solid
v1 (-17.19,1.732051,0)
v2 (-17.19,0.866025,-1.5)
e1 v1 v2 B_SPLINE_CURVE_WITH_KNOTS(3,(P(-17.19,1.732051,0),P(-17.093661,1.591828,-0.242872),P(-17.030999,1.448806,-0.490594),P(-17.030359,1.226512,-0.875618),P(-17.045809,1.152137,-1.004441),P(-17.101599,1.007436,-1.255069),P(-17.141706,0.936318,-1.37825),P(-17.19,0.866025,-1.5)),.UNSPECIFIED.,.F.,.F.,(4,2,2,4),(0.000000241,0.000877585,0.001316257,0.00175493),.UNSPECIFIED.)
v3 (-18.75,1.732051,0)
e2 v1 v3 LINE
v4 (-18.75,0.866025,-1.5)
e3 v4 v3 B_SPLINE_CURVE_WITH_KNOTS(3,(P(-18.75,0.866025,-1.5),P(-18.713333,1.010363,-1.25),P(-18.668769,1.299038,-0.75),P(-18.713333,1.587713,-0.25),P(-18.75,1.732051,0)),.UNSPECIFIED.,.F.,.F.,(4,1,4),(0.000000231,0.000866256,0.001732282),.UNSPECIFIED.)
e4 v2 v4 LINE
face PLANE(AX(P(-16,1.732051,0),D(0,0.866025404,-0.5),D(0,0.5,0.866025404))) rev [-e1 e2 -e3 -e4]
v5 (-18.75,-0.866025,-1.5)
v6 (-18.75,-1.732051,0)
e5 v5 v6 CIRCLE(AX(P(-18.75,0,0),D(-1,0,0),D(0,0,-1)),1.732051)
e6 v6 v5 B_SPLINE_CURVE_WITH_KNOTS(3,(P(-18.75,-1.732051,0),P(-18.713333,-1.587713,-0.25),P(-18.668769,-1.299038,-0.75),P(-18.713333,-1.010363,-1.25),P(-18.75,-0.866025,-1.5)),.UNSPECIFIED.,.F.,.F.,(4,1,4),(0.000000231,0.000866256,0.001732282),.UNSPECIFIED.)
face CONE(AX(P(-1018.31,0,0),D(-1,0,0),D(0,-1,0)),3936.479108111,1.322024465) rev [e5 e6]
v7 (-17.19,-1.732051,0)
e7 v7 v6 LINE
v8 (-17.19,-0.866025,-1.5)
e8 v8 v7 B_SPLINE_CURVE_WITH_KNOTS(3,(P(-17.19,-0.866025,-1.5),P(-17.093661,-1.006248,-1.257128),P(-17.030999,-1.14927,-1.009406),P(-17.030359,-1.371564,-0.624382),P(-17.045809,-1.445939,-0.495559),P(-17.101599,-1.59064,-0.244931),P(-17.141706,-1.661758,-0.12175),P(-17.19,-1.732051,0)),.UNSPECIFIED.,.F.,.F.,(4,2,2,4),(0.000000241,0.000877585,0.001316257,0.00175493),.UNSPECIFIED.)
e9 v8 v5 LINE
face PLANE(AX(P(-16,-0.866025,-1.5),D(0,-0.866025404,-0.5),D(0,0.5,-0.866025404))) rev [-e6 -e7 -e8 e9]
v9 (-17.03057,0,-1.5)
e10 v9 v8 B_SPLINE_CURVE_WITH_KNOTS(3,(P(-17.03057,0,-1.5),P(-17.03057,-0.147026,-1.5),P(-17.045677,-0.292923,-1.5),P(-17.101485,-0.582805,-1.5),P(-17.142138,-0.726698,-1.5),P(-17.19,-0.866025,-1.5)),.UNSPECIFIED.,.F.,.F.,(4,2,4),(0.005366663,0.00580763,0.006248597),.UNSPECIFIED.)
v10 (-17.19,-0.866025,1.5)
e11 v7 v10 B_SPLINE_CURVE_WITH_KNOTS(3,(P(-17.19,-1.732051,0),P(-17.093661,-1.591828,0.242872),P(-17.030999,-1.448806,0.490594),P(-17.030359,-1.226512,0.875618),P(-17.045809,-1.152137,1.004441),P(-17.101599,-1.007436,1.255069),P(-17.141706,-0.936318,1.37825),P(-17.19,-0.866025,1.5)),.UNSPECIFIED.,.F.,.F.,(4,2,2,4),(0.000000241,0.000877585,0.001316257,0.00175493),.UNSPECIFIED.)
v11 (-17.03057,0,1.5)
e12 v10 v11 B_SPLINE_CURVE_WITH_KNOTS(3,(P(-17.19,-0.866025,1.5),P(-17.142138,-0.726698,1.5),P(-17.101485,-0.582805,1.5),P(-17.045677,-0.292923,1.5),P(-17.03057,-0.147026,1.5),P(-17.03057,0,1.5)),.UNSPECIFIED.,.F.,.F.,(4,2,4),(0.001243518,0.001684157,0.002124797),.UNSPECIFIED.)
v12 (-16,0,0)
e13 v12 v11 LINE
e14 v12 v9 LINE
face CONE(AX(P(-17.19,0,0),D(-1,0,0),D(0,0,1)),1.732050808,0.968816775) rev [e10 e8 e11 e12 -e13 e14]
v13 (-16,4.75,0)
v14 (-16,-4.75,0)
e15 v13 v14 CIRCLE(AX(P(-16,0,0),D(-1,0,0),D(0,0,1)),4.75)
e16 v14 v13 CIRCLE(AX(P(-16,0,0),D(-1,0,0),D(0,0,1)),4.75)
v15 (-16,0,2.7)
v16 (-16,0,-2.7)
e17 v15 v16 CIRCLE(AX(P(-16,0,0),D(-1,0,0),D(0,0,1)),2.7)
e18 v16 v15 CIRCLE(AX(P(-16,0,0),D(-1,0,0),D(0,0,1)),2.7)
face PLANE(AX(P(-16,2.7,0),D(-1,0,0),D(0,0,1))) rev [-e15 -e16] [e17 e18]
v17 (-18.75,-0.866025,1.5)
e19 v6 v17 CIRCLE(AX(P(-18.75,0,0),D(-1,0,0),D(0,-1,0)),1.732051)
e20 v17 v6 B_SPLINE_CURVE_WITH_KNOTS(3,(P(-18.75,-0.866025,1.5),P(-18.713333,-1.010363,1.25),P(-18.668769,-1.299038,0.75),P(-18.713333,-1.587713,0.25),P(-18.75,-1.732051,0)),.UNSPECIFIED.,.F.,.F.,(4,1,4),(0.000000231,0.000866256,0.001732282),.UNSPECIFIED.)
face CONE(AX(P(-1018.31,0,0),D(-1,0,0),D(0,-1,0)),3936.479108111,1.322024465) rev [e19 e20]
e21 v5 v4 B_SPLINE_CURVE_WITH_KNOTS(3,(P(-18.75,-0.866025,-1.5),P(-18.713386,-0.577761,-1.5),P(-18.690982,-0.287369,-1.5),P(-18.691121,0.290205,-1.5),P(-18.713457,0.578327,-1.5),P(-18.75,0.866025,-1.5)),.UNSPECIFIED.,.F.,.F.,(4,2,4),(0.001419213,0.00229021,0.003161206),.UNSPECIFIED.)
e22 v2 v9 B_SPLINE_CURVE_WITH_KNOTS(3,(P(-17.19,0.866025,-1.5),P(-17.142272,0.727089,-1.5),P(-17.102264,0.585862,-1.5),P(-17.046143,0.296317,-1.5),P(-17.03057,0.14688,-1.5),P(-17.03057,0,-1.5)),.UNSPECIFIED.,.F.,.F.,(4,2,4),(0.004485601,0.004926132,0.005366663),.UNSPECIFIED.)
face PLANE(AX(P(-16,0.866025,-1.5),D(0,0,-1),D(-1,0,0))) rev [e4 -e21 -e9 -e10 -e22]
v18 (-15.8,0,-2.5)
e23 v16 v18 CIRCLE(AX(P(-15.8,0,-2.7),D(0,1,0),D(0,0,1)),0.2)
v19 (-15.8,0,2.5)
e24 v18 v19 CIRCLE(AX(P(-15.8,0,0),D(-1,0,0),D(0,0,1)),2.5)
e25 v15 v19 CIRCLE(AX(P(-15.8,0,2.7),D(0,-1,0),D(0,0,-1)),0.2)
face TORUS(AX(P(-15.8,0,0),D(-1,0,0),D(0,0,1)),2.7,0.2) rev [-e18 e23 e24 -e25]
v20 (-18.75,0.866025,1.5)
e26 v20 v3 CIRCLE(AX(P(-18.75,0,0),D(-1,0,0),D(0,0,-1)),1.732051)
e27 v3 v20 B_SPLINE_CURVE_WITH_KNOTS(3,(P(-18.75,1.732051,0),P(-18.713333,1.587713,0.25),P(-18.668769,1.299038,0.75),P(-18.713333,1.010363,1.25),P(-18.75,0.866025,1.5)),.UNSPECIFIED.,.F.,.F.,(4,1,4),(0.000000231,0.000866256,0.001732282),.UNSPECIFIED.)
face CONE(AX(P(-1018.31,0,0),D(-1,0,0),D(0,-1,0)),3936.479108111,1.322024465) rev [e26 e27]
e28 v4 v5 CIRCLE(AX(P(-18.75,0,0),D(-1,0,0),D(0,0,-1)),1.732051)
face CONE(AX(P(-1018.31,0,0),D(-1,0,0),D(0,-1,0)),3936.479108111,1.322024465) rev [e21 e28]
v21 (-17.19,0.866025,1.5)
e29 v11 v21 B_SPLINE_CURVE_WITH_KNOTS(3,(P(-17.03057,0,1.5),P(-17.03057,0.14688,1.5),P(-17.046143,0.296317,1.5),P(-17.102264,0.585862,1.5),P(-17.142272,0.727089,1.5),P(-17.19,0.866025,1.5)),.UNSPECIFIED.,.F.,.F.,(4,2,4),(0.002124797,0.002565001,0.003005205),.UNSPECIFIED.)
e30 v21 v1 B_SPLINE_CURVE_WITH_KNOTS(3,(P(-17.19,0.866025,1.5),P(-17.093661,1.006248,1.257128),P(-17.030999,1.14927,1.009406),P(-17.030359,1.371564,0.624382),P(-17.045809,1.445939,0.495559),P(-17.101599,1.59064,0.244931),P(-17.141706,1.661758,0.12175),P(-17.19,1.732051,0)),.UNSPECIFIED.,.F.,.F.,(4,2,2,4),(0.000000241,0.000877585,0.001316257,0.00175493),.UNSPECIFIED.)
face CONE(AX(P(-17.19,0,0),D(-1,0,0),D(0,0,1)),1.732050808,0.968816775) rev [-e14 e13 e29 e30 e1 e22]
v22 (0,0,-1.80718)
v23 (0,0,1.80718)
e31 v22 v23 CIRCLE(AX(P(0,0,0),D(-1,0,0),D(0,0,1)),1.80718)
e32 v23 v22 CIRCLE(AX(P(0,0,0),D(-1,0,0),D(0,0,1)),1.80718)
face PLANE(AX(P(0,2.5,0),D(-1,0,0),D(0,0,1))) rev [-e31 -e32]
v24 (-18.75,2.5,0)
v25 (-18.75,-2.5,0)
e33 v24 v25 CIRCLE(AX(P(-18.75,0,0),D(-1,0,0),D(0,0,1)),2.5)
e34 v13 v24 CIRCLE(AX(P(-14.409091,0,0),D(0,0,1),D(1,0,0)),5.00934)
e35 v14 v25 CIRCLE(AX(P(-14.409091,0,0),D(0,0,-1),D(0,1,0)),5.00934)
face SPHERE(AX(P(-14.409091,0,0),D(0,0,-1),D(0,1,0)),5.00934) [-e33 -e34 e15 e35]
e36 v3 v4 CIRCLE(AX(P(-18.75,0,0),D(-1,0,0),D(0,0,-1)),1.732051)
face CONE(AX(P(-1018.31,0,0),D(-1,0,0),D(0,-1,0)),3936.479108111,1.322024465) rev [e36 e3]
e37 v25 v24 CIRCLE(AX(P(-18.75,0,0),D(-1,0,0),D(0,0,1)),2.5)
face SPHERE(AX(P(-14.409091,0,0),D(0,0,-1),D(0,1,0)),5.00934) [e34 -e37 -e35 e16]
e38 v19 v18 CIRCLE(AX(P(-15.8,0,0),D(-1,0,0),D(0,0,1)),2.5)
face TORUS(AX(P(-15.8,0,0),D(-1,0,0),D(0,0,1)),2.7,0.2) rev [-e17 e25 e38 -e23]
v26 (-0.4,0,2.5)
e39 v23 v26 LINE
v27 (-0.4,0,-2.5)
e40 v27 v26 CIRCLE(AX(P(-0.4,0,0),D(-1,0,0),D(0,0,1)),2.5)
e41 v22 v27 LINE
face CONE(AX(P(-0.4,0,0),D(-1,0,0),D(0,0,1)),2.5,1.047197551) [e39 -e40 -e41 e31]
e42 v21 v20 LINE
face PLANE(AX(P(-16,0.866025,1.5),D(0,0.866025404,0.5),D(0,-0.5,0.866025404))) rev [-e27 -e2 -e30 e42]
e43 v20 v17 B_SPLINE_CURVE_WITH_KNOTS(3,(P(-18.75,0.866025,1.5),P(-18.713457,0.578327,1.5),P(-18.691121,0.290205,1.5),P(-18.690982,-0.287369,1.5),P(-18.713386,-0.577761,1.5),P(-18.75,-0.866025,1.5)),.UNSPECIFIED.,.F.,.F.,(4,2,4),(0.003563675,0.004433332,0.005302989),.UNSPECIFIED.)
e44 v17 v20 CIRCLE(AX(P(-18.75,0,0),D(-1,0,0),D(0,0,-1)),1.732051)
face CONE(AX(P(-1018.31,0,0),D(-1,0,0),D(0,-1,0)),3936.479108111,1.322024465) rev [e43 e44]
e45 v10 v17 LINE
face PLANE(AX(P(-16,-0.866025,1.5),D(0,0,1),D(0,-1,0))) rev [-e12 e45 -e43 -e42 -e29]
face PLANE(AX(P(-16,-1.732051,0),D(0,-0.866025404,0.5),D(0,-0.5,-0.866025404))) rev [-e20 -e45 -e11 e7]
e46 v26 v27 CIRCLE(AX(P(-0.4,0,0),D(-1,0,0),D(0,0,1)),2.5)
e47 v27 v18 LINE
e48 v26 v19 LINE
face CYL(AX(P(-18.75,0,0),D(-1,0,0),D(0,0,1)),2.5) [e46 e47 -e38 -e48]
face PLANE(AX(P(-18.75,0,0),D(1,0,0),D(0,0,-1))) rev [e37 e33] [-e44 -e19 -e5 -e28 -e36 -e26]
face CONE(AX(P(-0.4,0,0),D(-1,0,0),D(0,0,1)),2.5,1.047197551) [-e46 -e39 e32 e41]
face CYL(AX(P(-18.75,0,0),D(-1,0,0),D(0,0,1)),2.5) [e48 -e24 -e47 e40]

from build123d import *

# Parameters (mm, degrees)
CUT_EXTRUDE1_DEPTH = 2.75


with BuildPart() as part:
    # Sketch1 → Revolve1 (revolve)
    with BuildSketch(Plane.XY, mode=Mode.PRIVATE) as revolve1_sk:
        with BuildLine():
            Line((0, 2.5), (-15.8, 2.5))
            ThreePointArc((-15.8, 2.5), (-15.941421356, 2.558578644), (-16, 2.7))
            Line((-16, 2.7), (-16, 4.75))
            ThreePointArc((-16, 4.75), (-17.581194586, 3.877015605), (-18.75, 2.5))
            Line((-18.75, 2.5), (-18.75, 0))
            Line((-18.75, 0), (0, 0))
            Line((0, 0), (0, 2.5))
        make_face()
    revolve(revolve1_sk.sketch.rotate(Axis((-18.75, 0, 0), (1, 0, 0)), 90), axis=Axis((-18.75, 0, 0), (1, 0, 0)))

    # Sketch2 → Cut-Extrude1 (cut)
    with BuildSketch(Plane.ZY.offset(18.75)):
        Polygon((0, 1.732050808), (-1.5, 0.866025404), (-1.5, -0.866025404), (0, -1.732050808), (1.5, -0.866025404), (1.5, 0.866025404), align=None)
    extrude(amount=-CUT_EXTRUDE1_DEPTH, mode=Mode.SUBTRACT)

    # Sketch6 → Revolve2 (revolve)
    with BuildSketch(Plane.XY):
        Polygon((-17.19, 1.732050808), (-16, 0), (-15.56, 0), (-15.56, 1.732050808), align=None)
    revolve(axis=Axis((-18.75, 0, 0), (1, 0, 0)))

    # Sketch7 → Cut-Revolve5 (revolve, cut)
    with BuildSketch(Plane.XY):
        Polygon((-18.75, 1.732050808), (-18.31, 0), (-18.75, 0), align=None)
    revolve(axis=Axis((-18.75, 0, 0), (1, 0, 0)), mode=Mode.SUBTRACT)

    # Sketch4 → Cut-Revolve1 (revolve, cut)
    with BuildSketch(Plane.XY, mode=Mode.PRIVATE) as cut_revolve1_sk:
        Polygon((-0.4, 2.5), (0, 1.807179677), (0.4, 2.5), align=None)
    revolve(cut_revolve1_sk.sketch.rotate(Axis((-0.4, 0, 0), (1, 0, 0)), 90), axis=Axis((-0.4, 0, 0), (1, 0, 0)), mode=Mode.SUBTRACT)


solid = part.part
